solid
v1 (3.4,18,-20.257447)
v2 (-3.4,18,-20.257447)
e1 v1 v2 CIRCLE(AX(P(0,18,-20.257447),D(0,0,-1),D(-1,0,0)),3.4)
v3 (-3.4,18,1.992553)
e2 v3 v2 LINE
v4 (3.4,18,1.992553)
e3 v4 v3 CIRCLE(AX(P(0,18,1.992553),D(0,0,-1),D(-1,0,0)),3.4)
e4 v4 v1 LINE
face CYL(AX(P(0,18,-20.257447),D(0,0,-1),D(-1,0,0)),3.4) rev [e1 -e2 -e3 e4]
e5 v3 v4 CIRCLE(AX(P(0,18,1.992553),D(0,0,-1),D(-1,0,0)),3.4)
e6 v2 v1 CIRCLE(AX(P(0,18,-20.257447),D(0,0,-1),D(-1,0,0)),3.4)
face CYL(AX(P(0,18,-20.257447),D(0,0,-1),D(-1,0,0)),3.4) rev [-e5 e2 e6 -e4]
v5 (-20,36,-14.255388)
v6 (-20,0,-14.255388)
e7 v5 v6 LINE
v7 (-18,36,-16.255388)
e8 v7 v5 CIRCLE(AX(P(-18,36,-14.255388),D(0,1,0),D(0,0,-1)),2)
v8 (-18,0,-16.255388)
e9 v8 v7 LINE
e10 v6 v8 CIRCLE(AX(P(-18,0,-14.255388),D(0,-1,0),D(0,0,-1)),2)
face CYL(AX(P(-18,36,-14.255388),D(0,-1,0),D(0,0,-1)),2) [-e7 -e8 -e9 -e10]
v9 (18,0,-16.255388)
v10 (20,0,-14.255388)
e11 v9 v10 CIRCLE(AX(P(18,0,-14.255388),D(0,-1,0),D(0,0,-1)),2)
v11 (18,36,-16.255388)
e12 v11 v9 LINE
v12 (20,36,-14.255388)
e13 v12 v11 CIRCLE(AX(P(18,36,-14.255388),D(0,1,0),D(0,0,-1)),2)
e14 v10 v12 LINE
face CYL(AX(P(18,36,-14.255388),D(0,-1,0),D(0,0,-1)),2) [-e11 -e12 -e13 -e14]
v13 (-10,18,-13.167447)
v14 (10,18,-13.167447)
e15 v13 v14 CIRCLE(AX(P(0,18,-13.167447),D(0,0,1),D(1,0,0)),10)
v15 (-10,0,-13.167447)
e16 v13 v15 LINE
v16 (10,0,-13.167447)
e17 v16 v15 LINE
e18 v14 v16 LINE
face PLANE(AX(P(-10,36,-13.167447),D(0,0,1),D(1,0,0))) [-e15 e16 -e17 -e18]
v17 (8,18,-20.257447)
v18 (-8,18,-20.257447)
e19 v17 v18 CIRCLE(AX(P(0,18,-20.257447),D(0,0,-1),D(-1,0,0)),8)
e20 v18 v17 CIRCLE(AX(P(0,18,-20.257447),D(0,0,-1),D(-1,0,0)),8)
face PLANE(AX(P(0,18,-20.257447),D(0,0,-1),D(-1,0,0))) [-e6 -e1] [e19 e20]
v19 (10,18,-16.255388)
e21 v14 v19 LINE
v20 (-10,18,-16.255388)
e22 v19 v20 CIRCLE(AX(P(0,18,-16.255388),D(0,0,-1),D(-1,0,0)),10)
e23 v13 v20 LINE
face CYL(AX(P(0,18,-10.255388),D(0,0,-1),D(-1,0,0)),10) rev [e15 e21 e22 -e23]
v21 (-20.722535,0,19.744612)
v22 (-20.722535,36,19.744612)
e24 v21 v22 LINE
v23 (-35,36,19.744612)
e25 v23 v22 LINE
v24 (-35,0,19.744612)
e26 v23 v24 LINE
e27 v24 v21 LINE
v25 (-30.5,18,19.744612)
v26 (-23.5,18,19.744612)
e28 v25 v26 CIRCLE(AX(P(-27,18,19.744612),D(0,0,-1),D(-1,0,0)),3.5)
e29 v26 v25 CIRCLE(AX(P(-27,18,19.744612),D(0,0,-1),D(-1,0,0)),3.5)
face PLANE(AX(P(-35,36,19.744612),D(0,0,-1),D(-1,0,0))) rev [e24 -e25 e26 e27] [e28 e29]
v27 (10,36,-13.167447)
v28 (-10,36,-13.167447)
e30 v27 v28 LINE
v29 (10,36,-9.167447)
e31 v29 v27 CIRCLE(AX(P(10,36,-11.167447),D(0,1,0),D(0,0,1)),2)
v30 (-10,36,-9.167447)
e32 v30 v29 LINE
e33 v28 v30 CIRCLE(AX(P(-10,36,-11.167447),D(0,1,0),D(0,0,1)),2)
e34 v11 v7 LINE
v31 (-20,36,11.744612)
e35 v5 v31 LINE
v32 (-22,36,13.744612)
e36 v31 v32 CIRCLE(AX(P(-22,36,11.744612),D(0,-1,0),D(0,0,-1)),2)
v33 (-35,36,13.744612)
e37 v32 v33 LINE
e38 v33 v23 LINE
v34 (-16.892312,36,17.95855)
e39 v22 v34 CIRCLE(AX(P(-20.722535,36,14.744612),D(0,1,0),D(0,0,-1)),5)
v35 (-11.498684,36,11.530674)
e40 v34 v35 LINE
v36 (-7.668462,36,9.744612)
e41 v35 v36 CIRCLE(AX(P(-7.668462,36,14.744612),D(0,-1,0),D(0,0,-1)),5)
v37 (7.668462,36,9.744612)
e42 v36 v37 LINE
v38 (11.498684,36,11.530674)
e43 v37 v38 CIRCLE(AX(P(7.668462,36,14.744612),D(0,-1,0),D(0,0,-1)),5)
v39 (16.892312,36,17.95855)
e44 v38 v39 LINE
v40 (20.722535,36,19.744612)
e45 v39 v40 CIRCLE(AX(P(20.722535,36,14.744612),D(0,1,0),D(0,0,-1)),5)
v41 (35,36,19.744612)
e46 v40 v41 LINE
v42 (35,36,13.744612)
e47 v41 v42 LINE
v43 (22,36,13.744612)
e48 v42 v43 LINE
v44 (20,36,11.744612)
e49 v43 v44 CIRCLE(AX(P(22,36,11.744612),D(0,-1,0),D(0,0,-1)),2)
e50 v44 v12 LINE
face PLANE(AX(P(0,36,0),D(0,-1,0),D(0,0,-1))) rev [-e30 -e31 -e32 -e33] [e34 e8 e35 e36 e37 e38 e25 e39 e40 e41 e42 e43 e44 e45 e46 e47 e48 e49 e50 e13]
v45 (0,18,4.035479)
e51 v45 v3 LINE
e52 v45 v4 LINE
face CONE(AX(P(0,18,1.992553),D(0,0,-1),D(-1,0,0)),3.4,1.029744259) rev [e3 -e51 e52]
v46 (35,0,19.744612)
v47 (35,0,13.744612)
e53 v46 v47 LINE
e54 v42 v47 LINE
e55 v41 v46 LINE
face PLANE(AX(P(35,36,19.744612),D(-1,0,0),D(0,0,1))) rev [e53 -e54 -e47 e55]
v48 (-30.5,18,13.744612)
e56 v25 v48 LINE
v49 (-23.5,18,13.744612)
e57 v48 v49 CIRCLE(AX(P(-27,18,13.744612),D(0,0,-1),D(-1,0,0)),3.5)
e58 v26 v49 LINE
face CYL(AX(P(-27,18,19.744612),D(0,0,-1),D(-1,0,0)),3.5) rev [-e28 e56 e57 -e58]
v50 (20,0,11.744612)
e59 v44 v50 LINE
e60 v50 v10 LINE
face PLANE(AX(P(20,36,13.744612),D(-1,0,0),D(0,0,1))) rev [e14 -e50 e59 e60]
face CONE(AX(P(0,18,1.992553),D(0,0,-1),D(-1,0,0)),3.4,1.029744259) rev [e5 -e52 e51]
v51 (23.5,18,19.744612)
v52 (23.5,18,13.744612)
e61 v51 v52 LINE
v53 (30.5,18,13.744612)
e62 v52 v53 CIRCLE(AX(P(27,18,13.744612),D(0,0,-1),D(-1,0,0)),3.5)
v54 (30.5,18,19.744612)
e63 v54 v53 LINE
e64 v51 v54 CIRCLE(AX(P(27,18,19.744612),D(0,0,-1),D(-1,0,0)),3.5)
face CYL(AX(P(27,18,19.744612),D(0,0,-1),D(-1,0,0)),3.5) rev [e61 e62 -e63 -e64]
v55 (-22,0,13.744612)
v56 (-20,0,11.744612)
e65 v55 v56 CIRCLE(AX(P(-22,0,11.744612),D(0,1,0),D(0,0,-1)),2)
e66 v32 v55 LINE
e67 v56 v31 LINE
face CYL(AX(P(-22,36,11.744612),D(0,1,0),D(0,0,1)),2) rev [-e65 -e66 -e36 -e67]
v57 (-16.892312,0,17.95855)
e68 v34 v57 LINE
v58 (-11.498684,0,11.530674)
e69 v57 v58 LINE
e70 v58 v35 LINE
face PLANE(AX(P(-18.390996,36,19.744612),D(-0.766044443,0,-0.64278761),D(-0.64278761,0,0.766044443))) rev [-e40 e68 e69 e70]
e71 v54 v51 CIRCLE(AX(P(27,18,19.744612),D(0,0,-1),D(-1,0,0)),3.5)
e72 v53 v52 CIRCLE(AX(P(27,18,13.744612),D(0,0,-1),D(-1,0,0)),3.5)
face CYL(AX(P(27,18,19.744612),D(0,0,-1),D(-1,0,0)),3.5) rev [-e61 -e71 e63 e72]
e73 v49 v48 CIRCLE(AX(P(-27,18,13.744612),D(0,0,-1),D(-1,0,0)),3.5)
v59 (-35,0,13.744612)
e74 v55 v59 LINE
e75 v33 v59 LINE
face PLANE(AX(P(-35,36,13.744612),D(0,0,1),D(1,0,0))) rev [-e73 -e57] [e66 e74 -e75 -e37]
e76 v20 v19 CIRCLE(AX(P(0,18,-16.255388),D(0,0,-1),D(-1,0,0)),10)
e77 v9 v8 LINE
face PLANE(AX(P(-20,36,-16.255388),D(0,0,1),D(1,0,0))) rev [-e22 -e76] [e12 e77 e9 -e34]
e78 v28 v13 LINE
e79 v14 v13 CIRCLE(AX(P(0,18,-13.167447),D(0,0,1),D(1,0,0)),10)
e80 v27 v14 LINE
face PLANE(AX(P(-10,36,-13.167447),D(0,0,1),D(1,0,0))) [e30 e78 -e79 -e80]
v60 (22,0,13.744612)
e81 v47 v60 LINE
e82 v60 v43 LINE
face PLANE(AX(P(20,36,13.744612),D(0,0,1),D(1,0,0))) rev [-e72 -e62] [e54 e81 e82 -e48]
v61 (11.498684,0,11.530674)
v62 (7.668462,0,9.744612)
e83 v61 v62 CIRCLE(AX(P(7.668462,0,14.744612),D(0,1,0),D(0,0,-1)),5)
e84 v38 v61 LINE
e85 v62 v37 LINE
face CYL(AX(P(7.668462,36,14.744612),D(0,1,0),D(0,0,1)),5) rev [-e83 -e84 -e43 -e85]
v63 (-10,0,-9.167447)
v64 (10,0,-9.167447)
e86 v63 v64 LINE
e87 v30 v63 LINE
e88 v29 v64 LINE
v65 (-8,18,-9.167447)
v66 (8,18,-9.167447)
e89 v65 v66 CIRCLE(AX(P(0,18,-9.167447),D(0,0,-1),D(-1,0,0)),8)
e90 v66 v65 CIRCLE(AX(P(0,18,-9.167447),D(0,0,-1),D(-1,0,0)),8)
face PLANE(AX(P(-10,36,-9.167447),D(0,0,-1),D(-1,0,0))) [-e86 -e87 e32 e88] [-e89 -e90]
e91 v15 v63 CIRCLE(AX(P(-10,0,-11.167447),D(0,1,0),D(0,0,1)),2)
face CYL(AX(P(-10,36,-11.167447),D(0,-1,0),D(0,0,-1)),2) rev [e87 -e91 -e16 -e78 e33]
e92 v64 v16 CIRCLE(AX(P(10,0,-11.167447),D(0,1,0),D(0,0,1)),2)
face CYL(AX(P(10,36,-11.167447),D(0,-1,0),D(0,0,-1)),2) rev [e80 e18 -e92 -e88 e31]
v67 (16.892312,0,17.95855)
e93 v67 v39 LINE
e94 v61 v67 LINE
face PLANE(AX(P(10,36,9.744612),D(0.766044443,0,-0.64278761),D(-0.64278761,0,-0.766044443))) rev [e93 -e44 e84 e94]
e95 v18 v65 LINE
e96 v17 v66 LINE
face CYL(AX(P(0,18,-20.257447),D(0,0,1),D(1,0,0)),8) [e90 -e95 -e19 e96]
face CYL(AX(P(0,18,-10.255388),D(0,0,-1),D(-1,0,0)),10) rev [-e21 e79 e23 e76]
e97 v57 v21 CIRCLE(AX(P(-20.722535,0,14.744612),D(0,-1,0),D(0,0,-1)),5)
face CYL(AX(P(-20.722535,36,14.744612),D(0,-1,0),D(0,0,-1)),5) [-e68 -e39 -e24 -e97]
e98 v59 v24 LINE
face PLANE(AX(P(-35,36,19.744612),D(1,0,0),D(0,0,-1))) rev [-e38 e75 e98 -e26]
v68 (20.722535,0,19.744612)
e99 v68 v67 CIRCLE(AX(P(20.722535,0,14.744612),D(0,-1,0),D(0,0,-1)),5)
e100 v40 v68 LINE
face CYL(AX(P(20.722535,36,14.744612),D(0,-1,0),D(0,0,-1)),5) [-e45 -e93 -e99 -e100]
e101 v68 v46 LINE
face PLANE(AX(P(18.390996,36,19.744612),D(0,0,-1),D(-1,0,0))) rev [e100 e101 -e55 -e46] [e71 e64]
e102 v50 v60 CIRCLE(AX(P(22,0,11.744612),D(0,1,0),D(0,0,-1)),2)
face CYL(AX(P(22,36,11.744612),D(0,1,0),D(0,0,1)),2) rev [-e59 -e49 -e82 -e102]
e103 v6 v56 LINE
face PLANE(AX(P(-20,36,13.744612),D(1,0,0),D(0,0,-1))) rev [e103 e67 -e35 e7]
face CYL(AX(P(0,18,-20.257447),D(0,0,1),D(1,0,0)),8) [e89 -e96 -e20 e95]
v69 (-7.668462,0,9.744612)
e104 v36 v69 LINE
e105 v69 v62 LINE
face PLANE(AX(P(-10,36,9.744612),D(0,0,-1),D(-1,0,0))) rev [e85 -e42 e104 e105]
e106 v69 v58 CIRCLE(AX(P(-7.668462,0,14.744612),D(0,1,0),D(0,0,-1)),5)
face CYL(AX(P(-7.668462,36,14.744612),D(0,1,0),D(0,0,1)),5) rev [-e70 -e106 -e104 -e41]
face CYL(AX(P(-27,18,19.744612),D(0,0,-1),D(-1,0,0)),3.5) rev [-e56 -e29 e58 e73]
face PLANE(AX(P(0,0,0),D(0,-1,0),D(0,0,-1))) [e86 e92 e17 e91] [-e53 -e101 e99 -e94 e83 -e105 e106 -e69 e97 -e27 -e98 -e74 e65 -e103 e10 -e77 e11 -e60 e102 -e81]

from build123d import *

# Parameters (mm, degrees)
BOSS_EXTRUDE1_DEPTH   = 36
FILLET1_R             = 5
FILLET2_R             = 2
SKETCH2_R             = 3.5
CUT_EXTRUDE1_DEPTH    = 59.489315264
SKETCH3_R             = 10
CUT_EXTRUDE2_DEPTH    = 6
SKETCH4_R             = 8
BOSS_EXTRUDE2_DEPTH   = 11.09
M8_TAPPED_HOLE1_D     = 6.8
M8_TAPPED_HOLE1_DEPTH = 22.25
M8_TAPPED_HOLE1_TIP   = 2.042926105
FILLET3_R             = 2


with BuildPart() as part:
    # Sketch1 → Boss-Extrude1 (new body)
    with BuildSketch(Plane(origin=(0, 0, 0), x_dir=(1, 0, 0), z_dir=(0, 1, 0))):
        Polygon((-20, -13.744612069), (-20, 16.255387931), (20, 16.255387931), (20, -13.744612069), (35, -13.744612069), (35, -19.744612069), (18.390996312, -19.744612069), (10, -9.744612069), (-10, -9.744612069), (-18.390996312, -19.744612069), (-35, -19.744612069), (-35, -13.744612069), align=None)
        with BuildLine():
            Line((-10, 13.167446825), (10, 13.167446825))
            ThreePointArc((10, 13.167446825), (12, 11.167446825), (10, 9.167446825))
            Line((10, 9.167446825), (-10, 9.167446825))
            ThreePointArc((-10, 9.167446825), (-12, 11.167446825), (-10, 13.167446825))
        make_face(mode=Mode.SUBTRACT)
    extrude(amount=BOSS_EXTRUDE1_DEPTH)

    # Fillet1
    fillet1_edges = [part.edges().sort_by_distance(p)[0] for p in [
        (18.390996312, 18, 19.744612069),
        (10, 18, 9.744612069),
        (-10, 18, 9.744612069),
        (-18.390996312, 18, 19.744612069),
    ]]
    fillet(fillet1_edges, radius=FILLET1_R)

    # Fillet2
    fillet2_edges = [part.edges().sort_by_distance(p)[0] for p in [
        (20, 18, 13.744612069),
        (-20, 18, 13.744612069),
    ]]
    fillet(fillet2_edges, radius=FILLET2_R)

    # Sketch2 → Cut-Extrude1 (cut, through all)
    with BuildSketch(Plane(origin=(0, 0, 13.744612069), x_dir=(-1, 0, 0), z_dir=(0, 0, -1))):
        with Locations((-27, 18)):
            Circle(SKETCH2_R)
        with Locations((27, 18)):
            Circle(SKETCH2_R)
    extrude(amount=-CUT_EXTRUDE1_DEPTH, mode=Mode.SUBTRACT)

    # Sketch3 → Cut-Extrude2 (cut)
    with BuildSketch(Plane(origin=(0, 0, -16.255387931), x_dir=(-1, 0, 0), z_dir=(0, 0, -1))):
        with Locations((0, 18)):
            Circle(SKETCH3_R)
    extrude(amount=-CUT_EXTRUDE2_DEPTH, mode=Mode.SUBTRACT)

    # Sketch4 → Boss-Extrude2 (add)
    with BuildSketch(Plane(origin=(0, 0, -9.167446825), x_dir=(-1, 0, 0), z_dir=(0, 0, -1))):
        with Locations((0, 18)):
            Circle(SKETCH4_R)
    extrude(amount=BOSS_EXTRUDE2_DEPTH)

    # M8 Tapped Hole1
    with Locations(Plane(origin=(0, 0, -20.257446825), x_dir=(-1, 0, 0), z_dir=(0, 0, -1))):
        with Locations((0, 18)):
            Hole(M8_TAPPED_HOLE1_D / 2, depth=M8_TAPPED_HOLE1_DEPTH)
            with Locations((0, 0, -(M8_TAPPED_HOLE1_DEPTH + M8_TAPPED_HOLE1_TIP / 2))):  # 118° drill point
                Cone(0, M8_TAPPED_HOLE1_D / 2, M8_TAPPED_HOLE1_TIP, mode=Mode.SUBTRACT)

    # Fillet3
    fillet3_edges = [part.edges().sort_by_distance(p)[0] for p in [
        (-20, 18, -16.255387931),
        (20, 18, -16.255387931),
    ]]
    fillet(fillet3_edges, radius=FILLET3_R)


solid = part.part
